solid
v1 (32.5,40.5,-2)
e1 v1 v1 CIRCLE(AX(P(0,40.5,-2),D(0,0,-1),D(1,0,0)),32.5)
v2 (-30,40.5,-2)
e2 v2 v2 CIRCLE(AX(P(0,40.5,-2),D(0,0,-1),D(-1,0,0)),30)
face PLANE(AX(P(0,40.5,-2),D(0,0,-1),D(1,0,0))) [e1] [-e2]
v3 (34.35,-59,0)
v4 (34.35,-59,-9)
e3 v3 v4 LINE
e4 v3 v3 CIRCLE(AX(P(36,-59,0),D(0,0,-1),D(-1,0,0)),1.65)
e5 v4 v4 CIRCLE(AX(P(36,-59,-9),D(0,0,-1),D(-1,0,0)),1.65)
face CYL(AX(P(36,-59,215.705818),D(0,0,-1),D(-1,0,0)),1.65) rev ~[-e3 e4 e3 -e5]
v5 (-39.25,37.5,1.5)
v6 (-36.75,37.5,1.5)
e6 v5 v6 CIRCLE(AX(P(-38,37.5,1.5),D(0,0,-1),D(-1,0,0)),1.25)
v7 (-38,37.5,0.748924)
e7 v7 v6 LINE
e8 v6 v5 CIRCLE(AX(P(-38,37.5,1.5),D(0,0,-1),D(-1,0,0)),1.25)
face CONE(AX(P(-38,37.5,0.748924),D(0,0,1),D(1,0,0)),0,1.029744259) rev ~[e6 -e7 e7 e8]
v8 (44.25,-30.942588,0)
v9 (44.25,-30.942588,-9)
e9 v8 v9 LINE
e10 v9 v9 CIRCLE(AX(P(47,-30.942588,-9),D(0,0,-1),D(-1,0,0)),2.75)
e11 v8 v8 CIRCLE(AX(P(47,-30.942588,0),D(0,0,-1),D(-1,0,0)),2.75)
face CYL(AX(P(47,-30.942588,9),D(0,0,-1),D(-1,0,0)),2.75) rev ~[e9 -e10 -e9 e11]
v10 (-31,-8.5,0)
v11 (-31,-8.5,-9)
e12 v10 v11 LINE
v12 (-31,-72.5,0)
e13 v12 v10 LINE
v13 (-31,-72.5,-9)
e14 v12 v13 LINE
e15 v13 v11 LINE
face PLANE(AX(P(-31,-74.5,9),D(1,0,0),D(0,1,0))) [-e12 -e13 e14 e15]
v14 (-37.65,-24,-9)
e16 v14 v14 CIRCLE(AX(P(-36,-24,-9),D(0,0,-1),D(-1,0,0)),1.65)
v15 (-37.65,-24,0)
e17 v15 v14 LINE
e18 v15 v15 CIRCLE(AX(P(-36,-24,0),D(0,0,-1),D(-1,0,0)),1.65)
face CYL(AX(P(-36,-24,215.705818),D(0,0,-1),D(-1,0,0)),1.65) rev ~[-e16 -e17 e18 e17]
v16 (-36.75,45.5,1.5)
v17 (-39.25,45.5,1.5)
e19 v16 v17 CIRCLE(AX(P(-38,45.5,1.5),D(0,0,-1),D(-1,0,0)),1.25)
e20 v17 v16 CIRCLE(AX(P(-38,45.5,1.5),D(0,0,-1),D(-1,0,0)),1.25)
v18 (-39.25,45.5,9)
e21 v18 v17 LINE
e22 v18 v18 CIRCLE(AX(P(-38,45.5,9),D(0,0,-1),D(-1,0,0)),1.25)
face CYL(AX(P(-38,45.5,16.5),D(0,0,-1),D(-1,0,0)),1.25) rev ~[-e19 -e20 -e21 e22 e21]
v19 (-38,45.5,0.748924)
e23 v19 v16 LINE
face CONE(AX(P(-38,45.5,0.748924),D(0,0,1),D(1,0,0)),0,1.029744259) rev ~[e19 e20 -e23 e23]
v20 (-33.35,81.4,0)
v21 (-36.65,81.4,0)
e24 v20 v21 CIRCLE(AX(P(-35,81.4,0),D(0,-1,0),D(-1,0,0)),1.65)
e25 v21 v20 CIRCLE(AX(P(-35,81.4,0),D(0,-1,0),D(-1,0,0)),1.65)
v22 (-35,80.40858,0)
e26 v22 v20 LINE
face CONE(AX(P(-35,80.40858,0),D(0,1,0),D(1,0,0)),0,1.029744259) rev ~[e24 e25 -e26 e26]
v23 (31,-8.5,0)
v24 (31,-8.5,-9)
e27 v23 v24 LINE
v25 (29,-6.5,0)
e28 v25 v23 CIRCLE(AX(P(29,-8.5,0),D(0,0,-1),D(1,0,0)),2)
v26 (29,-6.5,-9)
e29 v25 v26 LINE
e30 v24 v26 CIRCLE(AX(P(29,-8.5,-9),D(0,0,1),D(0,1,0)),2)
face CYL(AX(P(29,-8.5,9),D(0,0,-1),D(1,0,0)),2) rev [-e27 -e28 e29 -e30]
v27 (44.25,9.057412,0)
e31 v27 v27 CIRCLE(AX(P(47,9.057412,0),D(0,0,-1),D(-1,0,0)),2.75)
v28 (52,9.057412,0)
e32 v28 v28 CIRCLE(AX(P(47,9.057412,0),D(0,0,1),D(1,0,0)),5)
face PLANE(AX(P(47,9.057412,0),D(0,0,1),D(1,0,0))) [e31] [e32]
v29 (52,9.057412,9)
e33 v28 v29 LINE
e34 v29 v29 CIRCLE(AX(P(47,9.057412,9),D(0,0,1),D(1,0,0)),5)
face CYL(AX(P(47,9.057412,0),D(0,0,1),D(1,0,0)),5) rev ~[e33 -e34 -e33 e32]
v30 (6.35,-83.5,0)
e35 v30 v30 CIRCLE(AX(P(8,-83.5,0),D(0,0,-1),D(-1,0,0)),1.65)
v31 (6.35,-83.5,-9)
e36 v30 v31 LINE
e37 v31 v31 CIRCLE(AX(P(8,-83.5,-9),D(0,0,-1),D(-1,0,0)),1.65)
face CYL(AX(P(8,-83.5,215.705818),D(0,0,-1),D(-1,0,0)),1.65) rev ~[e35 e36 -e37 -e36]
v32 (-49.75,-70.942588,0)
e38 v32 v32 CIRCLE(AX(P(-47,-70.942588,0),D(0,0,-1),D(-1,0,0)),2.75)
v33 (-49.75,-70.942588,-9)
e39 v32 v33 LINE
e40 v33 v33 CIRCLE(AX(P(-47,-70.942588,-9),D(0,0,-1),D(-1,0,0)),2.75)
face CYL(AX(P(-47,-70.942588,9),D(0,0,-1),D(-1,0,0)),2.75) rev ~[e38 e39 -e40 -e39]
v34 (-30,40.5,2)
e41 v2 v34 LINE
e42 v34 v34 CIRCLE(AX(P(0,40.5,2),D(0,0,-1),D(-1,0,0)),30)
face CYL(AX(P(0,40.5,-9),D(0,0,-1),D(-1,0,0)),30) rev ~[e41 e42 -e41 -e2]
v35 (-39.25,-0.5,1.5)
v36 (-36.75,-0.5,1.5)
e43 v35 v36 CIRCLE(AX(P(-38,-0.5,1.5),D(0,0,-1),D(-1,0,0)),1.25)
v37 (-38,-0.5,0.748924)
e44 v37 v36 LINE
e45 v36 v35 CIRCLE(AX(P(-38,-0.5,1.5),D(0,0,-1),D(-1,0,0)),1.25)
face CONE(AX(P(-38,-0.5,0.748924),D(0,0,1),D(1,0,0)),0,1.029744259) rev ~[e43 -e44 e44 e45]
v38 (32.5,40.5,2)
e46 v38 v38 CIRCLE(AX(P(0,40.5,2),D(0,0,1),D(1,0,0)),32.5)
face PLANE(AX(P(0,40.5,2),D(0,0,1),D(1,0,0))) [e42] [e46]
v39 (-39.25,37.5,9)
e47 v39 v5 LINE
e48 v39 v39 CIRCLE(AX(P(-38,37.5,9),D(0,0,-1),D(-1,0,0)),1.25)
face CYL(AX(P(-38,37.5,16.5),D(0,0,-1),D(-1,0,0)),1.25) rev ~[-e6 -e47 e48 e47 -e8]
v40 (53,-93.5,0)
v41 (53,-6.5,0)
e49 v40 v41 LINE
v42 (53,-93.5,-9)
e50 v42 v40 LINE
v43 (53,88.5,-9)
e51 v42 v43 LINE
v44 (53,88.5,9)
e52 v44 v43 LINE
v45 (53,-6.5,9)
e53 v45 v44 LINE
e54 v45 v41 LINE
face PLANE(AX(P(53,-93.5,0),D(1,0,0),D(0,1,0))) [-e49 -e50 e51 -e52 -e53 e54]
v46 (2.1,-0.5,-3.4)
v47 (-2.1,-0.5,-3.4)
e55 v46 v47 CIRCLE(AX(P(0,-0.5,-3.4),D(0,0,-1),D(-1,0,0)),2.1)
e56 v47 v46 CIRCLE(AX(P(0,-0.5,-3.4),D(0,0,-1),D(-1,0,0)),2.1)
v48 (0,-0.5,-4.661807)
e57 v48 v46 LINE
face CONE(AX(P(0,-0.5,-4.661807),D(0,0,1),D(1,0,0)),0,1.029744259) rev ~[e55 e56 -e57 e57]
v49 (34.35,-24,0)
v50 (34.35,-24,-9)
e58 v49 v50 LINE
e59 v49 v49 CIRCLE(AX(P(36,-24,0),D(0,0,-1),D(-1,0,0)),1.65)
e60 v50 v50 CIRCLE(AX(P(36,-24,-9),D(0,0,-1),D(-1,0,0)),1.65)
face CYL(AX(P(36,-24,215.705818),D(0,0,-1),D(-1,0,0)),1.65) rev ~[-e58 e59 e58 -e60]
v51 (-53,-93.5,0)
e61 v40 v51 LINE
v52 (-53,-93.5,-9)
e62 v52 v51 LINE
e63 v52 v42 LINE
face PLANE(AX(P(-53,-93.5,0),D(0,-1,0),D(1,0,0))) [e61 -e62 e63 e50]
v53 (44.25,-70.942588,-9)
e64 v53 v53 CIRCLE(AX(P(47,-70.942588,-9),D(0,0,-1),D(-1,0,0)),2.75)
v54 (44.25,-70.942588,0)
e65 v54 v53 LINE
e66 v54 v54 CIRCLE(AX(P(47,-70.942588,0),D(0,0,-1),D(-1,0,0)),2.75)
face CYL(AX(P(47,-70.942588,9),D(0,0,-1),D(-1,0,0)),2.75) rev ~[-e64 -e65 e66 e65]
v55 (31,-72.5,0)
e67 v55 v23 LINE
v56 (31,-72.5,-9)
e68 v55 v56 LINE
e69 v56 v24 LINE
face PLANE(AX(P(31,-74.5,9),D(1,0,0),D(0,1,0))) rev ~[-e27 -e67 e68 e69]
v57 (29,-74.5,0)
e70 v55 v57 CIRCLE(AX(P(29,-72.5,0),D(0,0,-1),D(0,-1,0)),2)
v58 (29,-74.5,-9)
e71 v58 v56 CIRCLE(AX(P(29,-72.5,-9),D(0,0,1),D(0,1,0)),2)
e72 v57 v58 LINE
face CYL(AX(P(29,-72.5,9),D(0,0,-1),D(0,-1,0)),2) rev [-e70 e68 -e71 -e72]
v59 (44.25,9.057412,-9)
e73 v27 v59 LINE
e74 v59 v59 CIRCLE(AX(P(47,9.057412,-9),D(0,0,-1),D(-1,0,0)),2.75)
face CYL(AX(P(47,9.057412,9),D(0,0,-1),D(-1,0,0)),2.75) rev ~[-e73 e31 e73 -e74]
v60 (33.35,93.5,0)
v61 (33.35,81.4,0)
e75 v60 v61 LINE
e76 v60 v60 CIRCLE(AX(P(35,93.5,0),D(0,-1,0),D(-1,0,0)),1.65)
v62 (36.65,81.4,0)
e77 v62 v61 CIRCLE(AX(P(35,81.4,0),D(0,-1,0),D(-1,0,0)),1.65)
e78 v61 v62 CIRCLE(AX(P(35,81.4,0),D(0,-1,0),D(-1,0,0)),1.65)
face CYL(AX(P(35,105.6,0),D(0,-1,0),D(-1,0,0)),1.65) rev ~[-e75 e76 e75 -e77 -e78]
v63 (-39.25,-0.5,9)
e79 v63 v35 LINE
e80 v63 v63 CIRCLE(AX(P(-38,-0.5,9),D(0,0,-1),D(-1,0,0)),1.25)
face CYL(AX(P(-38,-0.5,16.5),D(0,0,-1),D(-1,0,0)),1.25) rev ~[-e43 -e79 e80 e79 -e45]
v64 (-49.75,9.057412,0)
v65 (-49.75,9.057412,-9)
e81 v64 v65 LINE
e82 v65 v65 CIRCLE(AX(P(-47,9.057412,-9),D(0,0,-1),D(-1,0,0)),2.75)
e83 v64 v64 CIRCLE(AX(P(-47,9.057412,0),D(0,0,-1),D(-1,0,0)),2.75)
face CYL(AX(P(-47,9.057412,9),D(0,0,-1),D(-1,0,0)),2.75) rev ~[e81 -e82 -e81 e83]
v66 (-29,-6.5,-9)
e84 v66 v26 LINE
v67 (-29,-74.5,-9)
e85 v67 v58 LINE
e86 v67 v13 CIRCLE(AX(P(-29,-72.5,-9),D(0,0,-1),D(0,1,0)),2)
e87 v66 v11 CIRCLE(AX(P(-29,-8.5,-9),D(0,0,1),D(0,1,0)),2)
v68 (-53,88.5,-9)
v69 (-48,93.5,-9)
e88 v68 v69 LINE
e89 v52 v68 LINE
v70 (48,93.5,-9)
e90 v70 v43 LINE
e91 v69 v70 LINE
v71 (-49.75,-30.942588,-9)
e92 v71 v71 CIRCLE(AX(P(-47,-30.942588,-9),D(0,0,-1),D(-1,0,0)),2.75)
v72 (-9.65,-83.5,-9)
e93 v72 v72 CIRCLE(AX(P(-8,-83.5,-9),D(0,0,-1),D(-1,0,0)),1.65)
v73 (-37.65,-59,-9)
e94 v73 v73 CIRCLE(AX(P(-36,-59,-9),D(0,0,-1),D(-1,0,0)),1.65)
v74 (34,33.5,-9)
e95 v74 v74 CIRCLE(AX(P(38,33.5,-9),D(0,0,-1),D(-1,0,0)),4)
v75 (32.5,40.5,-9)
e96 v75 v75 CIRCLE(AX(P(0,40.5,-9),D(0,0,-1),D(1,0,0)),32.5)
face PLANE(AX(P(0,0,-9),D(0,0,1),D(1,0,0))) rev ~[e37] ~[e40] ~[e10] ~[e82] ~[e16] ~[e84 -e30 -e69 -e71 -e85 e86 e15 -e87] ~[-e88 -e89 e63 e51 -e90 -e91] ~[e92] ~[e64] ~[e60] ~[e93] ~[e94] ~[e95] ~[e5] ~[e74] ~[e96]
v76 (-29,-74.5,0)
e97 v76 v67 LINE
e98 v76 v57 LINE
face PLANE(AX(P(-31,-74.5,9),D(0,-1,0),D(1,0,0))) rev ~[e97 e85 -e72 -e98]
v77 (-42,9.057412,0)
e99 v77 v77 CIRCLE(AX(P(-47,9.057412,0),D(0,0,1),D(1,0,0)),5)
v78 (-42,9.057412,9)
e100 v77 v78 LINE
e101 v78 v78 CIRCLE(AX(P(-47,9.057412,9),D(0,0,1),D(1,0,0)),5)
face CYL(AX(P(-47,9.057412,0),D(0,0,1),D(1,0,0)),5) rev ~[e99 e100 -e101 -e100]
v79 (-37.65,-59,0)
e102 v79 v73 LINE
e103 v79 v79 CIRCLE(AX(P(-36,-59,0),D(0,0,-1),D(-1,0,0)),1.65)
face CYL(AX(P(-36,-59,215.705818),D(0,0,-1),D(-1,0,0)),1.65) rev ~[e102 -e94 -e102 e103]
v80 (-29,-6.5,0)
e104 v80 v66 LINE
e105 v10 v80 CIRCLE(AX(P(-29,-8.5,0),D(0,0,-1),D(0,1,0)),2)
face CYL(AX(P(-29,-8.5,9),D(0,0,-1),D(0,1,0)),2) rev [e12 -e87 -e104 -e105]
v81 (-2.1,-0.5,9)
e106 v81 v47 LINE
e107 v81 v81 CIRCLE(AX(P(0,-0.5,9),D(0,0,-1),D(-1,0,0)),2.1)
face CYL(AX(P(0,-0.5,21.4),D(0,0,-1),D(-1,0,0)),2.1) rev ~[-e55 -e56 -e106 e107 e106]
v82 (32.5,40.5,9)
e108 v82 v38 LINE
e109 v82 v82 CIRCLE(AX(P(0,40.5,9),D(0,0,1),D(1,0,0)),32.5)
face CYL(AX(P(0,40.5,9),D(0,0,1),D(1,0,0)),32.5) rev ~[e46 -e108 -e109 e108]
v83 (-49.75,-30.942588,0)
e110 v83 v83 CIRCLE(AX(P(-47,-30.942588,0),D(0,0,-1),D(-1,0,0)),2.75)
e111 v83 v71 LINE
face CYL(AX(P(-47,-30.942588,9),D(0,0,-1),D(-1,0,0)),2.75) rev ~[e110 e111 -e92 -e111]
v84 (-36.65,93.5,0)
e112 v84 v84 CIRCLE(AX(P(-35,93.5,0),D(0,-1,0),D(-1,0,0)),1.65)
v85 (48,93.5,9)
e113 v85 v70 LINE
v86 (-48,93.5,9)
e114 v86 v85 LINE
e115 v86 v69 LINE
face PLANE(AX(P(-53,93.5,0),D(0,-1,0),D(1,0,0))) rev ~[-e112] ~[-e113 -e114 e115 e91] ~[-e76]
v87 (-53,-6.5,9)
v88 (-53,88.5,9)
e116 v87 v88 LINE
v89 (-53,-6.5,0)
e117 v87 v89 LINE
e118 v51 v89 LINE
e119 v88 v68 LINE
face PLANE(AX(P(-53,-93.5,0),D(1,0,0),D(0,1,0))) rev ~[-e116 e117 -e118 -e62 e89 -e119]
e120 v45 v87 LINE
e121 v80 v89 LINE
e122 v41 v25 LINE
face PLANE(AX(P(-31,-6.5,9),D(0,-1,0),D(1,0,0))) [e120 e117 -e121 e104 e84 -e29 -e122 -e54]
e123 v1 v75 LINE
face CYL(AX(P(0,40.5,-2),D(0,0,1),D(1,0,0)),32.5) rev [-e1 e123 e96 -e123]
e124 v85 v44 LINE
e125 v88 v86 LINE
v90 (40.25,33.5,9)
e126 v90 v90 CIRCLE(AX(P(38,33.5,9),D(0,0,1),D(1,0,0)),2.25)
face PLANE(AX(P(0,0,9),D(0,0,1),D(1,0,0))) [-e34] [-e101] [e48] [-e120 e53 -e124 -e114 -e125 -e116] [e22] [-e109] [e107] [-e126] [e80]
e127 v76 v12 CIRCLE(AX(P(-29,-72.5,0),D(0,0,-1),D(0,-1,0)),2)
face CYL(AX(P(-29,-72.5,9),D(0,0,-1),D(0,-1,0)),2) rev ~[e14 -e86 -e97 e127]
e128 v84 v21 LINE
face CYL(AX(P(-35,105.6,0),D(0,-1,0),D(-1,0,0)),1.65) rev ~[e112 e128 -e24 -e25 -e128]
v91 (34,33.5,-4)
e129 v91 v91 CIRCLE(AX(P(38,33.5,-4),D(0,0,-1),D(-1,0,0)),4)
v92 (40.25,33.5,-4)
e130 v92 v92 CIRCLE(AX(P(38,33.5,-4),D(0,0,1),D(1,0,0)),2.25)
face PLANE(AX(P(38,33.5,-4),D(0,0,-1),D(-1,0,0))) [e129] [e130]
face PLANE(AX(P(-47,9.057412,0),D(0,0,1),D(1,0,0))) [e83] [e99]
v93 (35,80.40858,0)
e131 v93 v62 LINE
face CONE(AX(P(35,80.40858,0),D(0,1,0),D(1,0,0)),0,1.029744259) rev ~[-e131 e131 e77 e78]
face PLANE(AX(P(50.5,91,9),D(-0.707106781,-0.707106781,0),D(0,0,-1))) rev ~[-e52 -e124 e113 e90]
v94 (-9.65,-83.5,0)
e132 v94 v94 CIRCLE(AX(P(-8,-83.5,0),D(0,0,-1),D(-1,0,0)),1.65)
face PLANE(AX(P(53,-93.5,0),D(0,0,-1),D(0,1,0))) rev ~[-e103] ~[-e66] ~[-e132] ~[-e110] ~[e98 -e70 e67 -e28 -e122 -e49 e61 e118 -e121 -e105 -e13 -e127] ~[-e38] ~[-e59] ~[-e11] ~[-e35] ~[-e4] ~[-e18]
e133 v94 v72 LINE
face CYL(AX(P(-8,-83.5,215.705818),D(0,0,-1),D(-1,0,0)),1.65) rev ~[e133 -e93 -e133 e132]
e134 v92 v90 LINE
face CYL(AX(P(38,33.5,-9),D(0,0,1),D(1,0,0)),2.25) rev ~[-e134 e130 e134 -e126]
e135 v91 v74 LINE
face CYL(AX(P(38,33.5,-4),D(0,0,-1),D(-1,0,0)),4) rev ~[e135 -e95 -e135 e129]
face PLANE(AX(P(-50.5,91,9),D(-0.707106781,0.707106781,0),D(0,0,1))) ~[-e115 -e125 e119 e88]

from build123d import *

# Parameters (mm, degrees)
SKETCH1_W                                            = 106
SKETCH1_H                                            = 187
BOSS_EXTRUDE1_DEPTH                                  = 9
SKETCH2_R                                            = 30
CUT_EXTRUDE1_DEPTH                                   = 109.973620661
SKETCH3_R                                            = 32.5
CUT_EXTRUDE2_DEPTH                                   = 7
CUT_EXTRUDE3_START                                   = -7
SKETCH4_R                                            = 32.5
CUT_EXTRUDE3_DEPTH                                   = 7
SKETCH5_W                                            = 62
SKETCH5_H                                            = 68
CUT_EXTRUDE4_DEPTH                                   = 109.973620661
FILLET1_R                                            = 2
SKETCH6_W                                            = 9
SKETCH6_H                                            = 87
CUT_EXTRUDE5_DEPTH                                   = 142.630681704
M4_TAPPED_HOLE1_D                                    = 3.3
M4_TAPPED_HOLE2_D                                    = 3.3
M3_TAPPED_HOLE1_D                                    = 2.5
M3_TAPPED_HOLE1_DEPTH                                = 7.5
M3_TAPPED_HOLE1_TIP                                  = 0.751075774
CHAMFER1_SIZE                                        = 5
HOLE_SIZE_PER_SOCKET_HEAD_CAP_SCREW_TYPE_D           = 4.5
HOLE_SIZE_PER_SOCKET_HEAD_CAP_SCREW_TYPE_CBORE_D     = 8
HOLE_SIZE_PER_SOCKET_HEAD_CAP_SCREW_TYPE_CBORE_DEPTH = 5
HOLE_SIZE_PER_SOCKET_HEAD_CAP_SCREW_2_D              = 5.5
HOLE_SIZE_PER_SOCKET_HEAD_CAP_SCREW_2_CBORE_D        = 10
HOLE_SIZE_PER_SOCKET_HEAD_CAP_SCREW_2_CBORE_DEPTH    = 9
M5_TAPPED_HOLE1_D                                    = 4.2
M5_TAPPED_HOLE1_DEPTH                                = 12.4
M5_TAPPED_HOLE1_TIP                                  = 1.2618073
M4_TAPPED_HOLE3_D                                    = 3.3
M4_TAPPED_HOLE3_DEPTH                                = 12.1
M4_TAPPED_HOLE3_TIP                                  = 0.991420021


with BuildPart() as part:
    # Sketch1 → Boss-Extrude1 (new, symmetric)
    with BuildSketch(Plane.XY):
        Rectangle(SKETCH1_W, SKETCH1_H)
    extrude(amount=BOSS_EXTRUDE1_DEPTH, both=True)

    # Sketch2 → Cut-Extrude1 (cut, through all)
    with BuildSketch(Plane(origin=(0, 0, -9), x_dir=(-1, 0, 0), z_dir=(0, 0, -1))):
        with Locations((0, 40.5)):
            Circle(SKETCH2_R)
    extrude(amount=-CUT_EXTRUDE1_DEPTH, mode=Mode.SUBTRACT)

    # Sketch3 → Cut-Extrude2 (cut)
    with BuildSketch(Plane.XY.offset(9)):
        with Locations((0, 40.5)):
            Circle(SKETCH3_R)
    extrude(amount=-CUT_EXTRUDE2_DEPTH, mode=Mode.SUBTRACT)

    # Sketch4 → Cut-Extrude3 (cut)
    with BuildSketch(Plane(origin=(0, 0, -9), x_dir=(-1, 0, 0), z_dir=(0, 0, -1)).offset(CUT_EXTRUDE3_START)):
        with Locations(Location((0, 40.5, 0), (0, 0, 180))):
            Circle(SKETCH4_R)
    extrude(amount=CUT_EXTRUDE3_DEPTH, mode=Mode.SUBTRACT)

    # Sketch5 → Cut-Extrude4 (cut, through all)
    with BuildSketch(Plane.XY.offset(9)):
        with Locations((0, -40.5)):
            Rectangle(SKETCH5_W, SKETCH5_H)
    extrude(amount=-CUT_EXTRUDE4_DEPTH, mode=Mode.SUBTRACT)

    # Fillet1
    fillet1_edges = [part.edges().sort_by_distance(p)[0] for p in [
        (-31, -74.5, 0),
        (-31, -6.5, 0),
        (31, -6.5, 0),
        (31, -74.5, 0),
    ]]
    fillet(fillet1_edges, radius=FILLET1_R)

    # Sketch6 → Cut-Extrude5 (cut, through all)
    with BuildSketch(Plane(origin=(53, 0, 0), x_dir=(0, 0, -1), z_dir=(1, 0, 0))):
        with Locations((-4.5, -50)):
            Rectangle(SKETCH6_W, SKETCH6_H)
    extrude(amount=-CUT_EXTRUDE5_DEPTH, mode=Mode.SUBTRACT)

    # M4 Tapped Hole1 (through all)
    with Locations(Plane.XY):
        with Locations((36, -24), (36, -59), (-36, -59), (-36, -24)):
            Hole(M4_TAPPED_HOLE1_D / 2)

    # M4 Tapped Hole2 (through all)
    with Locations(Plane.XY):
        with Locations((-8, -83.5), (8, -83.5)):
            Hole(M4_TAPPED_HOLE2_D / 2)

    # M3 Tapped Hole1
    with Locations(Plane.XY.offset(9)):
        with Locations((-38, 45.5), (-38, 37.5), (-38, -0.5)):
            Hole(M3_TAPPED_HOLE1_D / 2, depth=M3_TAPPED_HOLE1_DEPTH)
            with Locations((0, 0, -(M3_TAPPED_HOLE1_DEPTH + M3_TAPPED_HOLE1_TIP / 2))):  # 118° drill point
                Cone(0, M3_TAPPED_HOLE1_D / 2, M3_TAPPED_HOLE1_TIP, mode=Mode.SUBTRACT)

    # Chamfer1
    chamfer1_edges = [part.edges().sort_by_distance(p)[0] for p in [
        (-53, 93.5, 0),
        (53, 93.5, 0),
    ]]
    chamfer(chamfer1_edges, length=CHAMFER1_SIZE)

    # Hole size per socket head cap screw type (through all)
    with Locations(Plane(origin=(0, 0, -9), x_dir=(-1, 0, 0), z_dir=(0, 0, -1))):
        with Locations((-38, 33.5)):
            CounterBoreHole(HOLE_SIZE_PER_SOCKET_HEAD_CAP_SCREW_TYPE_D / 2, HOLE_SIZE_PER_SOCKET_HEAD_CAP_SCREW_TYPE_CBORE_D / 2, HOLE_SIZE_PER_SOCKET_HEAD_CAP_SCREW_TYPE_CBORE_DEPTH)

    # Hole size per socket head cap screw  2 (through all)
    with Locations(Plane.XY.offset(9)):
        with Locations((-47, 9.05741234), (-47, -30.94258766), (-47, -70.94258766), (47, -70.94258766), (47, -30.94258766), (47, 9.05741234)):
            CounterBoreHole(HOLE_SIZE_PER_SOCKET_HEAD_CAP_SCREW_2_D / 2, HOLE_SIZE_PER_SOCKET_HEAD_CAP_SCREW_2_CBORE_D / 2, HOLE_SIZE_PER_SOCKET_HEAD_CAP_SCREW_2_CBORE_DEPTH)

    # M5 Tapped Hole1
    with Locations(Plane.XY.offset(9)):
        with Locations((0, -0.5)):
            Hole(M5_TAPPED_HOLE1_D / 2, depth=M5_TAPPED_HOLE1_DEPTH)
            with Locations((0, 0, -(M5_TAPPED_HOLE1_DEPTH + M5_TAPPED_HOLE1_TIP / 2))):  # 118° drill point
                Cone(0, M5_TAPPED_HOLE1_D / 2, M5_TAPPED_HOLE1_TIP, mode=Mode.SUBTRACT)

    # M4 Tapped Hole3
    with Locations(Plane(origin=(0, 93.5, 0), x_dir=(1, 0, 0), z_dir=(0, 1, 0))):
        with Locations((-35, 0), (35, 0)):
            Hole(M4_TAPPED_HOLE3_D / 2, depth=M4_TAPPED_HOLE3_DEPTH)
            with Locations((0, 0, -(M4_TAPPED_HOLE3_DEPTH + M4_TAPPED_HOLE3_TIP / 2))):  # 118° drill point
                Cone(0, M4_TAPPED_HOLE3_D / 2, M4_TAPPED_HOLE3_TIP, mode=Mode.SUBTRACT)


solid = part.part
